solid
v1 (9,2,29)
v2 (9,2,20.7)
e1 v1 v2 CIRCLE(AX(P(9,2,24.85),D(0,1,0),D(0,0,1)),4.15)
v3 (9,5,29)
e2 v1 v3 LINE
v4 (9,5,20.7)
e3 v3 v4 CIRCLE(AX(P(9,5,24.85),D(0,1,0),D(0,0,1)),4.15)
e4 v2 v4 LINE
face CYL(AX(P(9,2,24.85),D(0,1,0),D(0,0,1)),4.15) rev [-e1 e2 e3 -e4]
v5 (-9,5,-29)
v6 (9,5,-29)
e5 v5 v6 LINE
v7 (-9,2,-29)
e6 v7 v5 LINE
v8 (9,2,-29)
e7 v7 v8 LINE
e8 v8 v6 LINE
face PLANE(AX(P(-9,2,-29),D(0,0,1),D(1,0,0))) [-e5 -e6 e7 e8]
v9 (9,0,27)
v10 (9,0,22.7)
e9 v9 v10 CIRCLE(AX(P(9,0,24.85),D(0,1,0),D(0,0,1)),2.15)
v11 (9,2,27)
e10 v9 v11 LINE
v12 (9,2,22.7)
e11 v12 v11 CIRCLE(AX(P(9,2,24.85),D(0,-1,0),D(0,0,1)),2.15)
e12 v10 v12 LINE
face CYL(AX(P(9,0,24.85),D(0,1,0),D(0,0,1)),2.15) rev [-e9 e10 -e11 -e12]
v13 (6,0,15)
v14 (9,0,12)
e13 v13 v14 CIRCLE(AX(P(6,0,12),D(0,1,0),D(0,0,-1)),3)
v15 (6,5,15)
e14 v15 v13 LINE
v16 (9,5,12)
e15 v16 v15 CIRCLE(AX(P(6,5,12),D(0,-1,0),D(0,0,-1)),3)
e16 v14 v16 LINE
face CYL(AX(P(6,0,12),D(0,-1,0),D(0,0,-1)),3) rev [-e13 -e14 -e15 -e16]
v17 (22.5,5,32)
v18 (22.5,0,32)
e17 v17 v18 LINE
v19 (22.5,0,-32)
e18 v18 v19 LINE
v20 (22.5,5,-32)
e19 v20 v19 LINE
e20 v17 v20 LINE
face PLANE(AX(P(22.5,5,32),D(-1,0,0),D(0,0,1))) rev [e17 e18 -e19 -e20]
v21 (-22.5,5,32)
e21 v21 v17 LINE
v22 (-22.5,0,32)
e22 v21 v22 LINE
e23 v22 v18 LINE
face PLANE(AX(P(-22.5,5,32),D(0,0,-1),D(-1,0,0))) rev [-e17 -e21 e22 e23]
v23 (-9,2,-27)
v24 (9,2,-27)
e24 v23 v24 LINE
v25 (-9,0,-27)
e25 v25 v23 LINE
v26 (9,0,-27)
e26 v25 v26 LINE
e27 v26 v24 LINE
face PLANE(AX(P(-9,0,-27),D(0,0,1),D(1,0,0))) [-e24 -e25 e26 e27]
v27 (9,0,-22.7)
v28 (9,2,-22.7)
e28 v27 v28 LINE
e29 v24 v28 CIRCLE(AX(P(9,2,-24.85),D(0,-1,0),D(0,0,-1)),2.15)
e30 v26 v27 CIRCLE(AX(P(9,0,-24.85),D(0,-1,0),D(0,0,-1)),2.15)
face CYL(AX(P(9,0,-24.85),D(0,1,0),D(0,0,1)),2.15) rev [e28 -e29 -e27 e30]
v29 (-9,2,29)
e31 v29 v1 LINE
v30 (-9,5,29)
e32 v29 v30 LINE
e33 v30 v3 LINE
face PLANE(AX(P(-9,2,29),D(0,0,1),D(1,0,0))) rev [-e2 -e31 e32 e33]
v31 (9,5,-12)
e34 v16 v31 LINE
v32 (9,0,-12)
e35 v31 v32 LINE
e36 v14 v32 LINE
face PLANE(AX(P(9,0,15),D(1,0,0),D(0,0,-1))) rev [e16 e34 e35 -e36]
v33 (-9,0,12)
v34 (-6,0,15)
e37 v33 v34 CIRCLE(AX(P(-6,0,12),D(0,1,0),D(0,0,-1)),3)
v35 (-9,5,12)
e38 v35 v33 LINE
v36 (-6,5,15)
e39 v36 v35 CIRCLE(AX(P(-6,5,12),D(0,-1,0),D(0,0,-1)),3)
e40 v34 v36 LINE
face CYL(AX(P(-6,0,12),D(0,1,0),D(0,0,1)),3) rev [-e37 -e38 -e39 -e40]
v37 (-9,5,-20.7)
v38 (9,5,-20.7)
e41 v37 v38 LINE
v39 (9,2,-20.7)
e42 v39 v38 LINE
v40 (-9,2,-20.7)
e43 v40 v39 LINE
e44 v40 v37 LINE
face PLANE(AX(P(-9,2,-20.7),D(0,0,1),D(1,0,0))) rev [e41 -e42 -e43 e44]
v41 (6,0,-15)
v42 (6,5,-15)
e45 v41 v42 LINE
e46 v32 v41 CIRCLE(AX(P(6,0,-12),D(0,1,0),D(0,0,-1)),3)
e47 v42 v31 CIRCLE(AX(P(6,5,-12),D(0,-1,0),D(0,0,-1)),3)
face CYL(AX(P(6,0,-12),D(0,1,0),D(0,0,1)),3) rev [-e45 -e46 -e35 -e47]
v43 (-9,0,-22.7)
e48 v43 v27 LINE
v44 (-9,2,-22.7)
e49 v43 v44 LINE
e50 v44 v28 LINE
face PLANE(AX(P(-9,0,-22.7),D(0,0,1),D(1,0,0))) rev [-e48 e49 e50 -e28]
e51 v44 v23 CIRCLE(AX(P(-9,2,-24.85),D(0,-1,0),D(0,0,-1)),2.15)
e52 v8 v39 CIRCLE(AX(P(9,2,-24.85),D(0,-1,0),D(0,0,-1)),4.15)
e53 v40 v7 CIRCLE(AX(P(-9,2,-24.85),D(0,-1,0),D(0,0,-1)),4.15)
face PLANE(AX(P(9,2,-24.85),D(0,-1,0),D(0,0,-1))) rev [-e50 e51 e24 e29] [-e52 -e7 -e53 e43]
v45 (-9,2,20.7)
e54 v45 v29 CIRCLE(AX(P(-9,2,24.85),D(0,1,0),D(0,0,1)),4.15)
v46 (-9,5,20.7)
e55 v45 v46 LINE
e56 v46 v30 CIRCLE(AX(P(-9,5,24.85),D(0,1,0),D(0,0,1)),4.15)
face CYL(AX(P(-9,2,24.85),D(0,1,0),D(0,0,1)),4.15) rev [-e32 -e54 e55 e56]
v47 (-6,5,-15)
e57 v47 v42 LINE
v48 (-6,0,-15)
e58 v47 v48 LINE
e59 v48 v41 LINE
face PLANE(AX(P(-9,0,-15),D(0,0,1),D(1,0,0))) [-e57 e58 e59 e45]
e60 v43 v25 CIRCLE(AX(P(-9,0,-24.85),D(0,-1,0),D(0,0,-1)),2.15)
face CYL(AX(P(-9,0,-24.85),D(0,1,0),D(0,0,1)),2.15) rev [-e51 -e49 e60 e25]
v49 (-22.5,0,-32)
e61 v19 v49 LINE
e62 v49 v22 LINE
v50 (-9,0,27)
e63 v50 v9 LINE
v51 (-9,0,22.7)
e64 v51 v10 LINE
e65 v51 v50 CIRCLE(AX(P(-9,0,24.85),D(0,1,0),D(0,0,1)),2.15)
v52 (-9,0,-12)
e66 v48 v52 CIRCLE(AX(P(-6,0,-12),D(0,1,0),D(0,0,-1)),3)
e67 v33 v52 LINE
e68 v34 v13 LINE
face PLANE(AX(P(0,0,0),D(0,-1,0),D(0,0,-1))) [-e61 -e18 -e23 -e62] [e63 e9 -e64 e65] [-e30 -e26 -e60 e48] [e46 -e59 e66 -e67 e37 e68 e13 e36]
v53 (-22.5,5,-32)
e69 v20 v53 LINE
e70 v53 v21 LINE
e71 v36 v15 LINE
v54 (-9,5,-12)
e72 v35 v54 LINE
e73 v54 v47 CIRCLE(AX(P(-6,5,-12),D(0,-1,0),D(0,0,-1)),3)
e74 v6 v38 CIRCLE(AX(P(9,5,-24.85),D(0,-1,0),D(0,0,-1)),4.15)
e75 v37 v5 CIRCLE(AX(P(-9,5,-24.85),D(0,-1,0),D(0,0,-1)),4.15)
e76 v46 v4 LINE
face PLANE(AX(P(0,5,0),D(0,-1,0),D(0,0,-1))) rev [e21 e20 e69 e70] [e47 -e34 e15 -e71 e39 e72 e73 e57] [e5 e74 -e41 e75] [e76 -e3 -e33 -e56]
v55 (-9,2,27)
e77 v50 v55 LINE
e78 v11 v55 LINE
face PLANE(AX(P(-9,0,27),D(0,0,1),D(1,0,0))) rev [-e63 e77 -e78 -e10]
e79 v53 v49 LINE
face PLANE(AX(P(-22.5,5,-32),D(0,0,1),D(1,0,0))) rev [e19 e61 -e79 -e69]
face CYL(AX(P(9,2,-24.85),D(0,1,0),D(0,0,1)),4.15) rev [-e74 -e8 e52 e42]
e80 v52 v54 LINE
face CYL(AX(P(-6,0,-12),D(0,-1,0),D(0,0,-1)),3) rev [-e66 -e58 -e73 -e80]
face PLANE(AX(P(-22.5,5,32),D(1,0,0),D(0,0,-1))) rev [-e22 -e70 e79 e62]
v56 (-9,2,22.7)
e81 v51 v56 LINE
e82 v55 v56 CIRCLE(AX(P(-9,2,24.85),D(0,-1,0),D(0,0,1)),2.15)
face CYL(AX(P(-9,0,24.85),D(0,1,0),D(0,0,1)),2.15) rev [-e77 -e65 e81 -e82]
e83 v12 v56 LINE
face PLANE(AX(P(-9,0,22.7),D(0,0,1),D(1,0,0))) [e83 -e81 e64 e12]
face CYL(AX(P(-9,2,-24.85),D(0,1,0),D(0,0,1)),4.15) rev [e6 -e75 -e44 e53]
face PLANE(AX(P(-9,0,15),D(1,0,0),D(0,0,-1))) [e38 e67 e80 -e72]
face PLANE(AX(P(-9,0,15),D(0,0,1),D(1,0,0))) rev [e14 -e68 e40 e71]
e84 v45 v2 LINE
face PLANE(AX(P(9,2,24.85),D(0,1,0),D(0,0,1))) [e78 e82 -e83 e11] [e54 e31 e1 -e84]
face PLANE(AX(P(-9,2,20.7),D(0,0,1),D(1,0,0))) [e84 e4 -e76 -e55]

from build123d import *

# Parameters (mm, degrees)
SKETCH1_W           = 45
SKETCH1_H           = 64
BOSS_EXTRUDE1_DEPTH = 5
SKETCH_2_3_W        = 18
SKETCH_2_3_H        = 30
CUT_EXTRUDE1_DEPTH  = 40.436658073
CUT_EXTRUDE2_DEPTH  = 3
FILLET1_R           = 3


with BuildPart() as part:
    # Sketch1 → Boss-Extrude1 (new body)
    with BuildSketch(Plane(origin=(0, 0, 0), x_dir=(1, 0, 0), z_dir=(0, 1, 0))):
        Rectangle(SKETCH1_W, SKETCH1_H)
    extrude(amount=BOSS_EXTRUDE1_DEPTH)

    # Sketch 2_3 → Cut-Extrude1 (cut, through all)
    with BuildSketch(Plane(origin=(0, 5, 0), x_dir=(1, 0, 0), z_dir=(0, 1, 0))):
        Rectangle(SKETCH_2_3_W, SKETCH_2_3_H)
        with BuildLine():
            Line((-9, -22.7), (9, -22.7))
            ThreePointArc((9, -22.7), (11.15, -24.85), (9, -27))
            Line((9, -27), (-9, -27))
            ThreePointArc((-9, -27), (-11.15, -24.85), (-9, -22.7))
        make_face()
        with BuildLine():
            Line((-9, 22.7), (9, 22.7))
            ThreePointArc((9, 22.7), (11.15, 24.85), (9, 27))
            Line((9, 27), (-9, 27))
            ThreePointArc((-9, 27), (-11.15, 24.85), (-9, 22.7))
        make_face()
    extrude(amount=-CUT_EXTRUDE1_DEPTH, mode=Mode.SUBTRACT)

    # Sketch 2_3 2 → Cut-Extrude2 (cut)
    with BuildSketch(Plane(origin=(0, 5, 0), x_dir=(1, 0, 0), z_dir=(0, 1, 0))):
        with BuildLine():
            Line((-9, -20.7), (9, -20.7))
            ThreePointArc((9, -20.7), (13.15, -24.85), (9, -29))
            Line((9, -29), (-9, -29))
            ThreePointArc((-9, -29), (-13.15, -24.85), (-9, -20.7))
        make_face()
        with BuildLine():
            Line((-9, 20.7), (9, 20.7))
            ThreePointArc((9, 20.7), (13.15, 24.85), (9, 29))
            Line((9, 29), (-9, 29))
            ThreePointArc((-9, 29), (-13.15, 24.85), (-9, 20.7))
        make_face()
    extrude(amount=-CUT_EXTRUDE2_DEPTH, mode=Mode.SUBTRACT)

    # Fillet1
    fillet1_edges = [part.edges().sort_by_distance(p)[0] for p in [
        (-9, 2.5, -15),
        (9, 2.5, -15),
        (9, 2.5, 15),
        (-9, 2.5, 15),
    ]]
    fillet(fillet1_edges, radius=FILLET1_R)


solid = part.part
